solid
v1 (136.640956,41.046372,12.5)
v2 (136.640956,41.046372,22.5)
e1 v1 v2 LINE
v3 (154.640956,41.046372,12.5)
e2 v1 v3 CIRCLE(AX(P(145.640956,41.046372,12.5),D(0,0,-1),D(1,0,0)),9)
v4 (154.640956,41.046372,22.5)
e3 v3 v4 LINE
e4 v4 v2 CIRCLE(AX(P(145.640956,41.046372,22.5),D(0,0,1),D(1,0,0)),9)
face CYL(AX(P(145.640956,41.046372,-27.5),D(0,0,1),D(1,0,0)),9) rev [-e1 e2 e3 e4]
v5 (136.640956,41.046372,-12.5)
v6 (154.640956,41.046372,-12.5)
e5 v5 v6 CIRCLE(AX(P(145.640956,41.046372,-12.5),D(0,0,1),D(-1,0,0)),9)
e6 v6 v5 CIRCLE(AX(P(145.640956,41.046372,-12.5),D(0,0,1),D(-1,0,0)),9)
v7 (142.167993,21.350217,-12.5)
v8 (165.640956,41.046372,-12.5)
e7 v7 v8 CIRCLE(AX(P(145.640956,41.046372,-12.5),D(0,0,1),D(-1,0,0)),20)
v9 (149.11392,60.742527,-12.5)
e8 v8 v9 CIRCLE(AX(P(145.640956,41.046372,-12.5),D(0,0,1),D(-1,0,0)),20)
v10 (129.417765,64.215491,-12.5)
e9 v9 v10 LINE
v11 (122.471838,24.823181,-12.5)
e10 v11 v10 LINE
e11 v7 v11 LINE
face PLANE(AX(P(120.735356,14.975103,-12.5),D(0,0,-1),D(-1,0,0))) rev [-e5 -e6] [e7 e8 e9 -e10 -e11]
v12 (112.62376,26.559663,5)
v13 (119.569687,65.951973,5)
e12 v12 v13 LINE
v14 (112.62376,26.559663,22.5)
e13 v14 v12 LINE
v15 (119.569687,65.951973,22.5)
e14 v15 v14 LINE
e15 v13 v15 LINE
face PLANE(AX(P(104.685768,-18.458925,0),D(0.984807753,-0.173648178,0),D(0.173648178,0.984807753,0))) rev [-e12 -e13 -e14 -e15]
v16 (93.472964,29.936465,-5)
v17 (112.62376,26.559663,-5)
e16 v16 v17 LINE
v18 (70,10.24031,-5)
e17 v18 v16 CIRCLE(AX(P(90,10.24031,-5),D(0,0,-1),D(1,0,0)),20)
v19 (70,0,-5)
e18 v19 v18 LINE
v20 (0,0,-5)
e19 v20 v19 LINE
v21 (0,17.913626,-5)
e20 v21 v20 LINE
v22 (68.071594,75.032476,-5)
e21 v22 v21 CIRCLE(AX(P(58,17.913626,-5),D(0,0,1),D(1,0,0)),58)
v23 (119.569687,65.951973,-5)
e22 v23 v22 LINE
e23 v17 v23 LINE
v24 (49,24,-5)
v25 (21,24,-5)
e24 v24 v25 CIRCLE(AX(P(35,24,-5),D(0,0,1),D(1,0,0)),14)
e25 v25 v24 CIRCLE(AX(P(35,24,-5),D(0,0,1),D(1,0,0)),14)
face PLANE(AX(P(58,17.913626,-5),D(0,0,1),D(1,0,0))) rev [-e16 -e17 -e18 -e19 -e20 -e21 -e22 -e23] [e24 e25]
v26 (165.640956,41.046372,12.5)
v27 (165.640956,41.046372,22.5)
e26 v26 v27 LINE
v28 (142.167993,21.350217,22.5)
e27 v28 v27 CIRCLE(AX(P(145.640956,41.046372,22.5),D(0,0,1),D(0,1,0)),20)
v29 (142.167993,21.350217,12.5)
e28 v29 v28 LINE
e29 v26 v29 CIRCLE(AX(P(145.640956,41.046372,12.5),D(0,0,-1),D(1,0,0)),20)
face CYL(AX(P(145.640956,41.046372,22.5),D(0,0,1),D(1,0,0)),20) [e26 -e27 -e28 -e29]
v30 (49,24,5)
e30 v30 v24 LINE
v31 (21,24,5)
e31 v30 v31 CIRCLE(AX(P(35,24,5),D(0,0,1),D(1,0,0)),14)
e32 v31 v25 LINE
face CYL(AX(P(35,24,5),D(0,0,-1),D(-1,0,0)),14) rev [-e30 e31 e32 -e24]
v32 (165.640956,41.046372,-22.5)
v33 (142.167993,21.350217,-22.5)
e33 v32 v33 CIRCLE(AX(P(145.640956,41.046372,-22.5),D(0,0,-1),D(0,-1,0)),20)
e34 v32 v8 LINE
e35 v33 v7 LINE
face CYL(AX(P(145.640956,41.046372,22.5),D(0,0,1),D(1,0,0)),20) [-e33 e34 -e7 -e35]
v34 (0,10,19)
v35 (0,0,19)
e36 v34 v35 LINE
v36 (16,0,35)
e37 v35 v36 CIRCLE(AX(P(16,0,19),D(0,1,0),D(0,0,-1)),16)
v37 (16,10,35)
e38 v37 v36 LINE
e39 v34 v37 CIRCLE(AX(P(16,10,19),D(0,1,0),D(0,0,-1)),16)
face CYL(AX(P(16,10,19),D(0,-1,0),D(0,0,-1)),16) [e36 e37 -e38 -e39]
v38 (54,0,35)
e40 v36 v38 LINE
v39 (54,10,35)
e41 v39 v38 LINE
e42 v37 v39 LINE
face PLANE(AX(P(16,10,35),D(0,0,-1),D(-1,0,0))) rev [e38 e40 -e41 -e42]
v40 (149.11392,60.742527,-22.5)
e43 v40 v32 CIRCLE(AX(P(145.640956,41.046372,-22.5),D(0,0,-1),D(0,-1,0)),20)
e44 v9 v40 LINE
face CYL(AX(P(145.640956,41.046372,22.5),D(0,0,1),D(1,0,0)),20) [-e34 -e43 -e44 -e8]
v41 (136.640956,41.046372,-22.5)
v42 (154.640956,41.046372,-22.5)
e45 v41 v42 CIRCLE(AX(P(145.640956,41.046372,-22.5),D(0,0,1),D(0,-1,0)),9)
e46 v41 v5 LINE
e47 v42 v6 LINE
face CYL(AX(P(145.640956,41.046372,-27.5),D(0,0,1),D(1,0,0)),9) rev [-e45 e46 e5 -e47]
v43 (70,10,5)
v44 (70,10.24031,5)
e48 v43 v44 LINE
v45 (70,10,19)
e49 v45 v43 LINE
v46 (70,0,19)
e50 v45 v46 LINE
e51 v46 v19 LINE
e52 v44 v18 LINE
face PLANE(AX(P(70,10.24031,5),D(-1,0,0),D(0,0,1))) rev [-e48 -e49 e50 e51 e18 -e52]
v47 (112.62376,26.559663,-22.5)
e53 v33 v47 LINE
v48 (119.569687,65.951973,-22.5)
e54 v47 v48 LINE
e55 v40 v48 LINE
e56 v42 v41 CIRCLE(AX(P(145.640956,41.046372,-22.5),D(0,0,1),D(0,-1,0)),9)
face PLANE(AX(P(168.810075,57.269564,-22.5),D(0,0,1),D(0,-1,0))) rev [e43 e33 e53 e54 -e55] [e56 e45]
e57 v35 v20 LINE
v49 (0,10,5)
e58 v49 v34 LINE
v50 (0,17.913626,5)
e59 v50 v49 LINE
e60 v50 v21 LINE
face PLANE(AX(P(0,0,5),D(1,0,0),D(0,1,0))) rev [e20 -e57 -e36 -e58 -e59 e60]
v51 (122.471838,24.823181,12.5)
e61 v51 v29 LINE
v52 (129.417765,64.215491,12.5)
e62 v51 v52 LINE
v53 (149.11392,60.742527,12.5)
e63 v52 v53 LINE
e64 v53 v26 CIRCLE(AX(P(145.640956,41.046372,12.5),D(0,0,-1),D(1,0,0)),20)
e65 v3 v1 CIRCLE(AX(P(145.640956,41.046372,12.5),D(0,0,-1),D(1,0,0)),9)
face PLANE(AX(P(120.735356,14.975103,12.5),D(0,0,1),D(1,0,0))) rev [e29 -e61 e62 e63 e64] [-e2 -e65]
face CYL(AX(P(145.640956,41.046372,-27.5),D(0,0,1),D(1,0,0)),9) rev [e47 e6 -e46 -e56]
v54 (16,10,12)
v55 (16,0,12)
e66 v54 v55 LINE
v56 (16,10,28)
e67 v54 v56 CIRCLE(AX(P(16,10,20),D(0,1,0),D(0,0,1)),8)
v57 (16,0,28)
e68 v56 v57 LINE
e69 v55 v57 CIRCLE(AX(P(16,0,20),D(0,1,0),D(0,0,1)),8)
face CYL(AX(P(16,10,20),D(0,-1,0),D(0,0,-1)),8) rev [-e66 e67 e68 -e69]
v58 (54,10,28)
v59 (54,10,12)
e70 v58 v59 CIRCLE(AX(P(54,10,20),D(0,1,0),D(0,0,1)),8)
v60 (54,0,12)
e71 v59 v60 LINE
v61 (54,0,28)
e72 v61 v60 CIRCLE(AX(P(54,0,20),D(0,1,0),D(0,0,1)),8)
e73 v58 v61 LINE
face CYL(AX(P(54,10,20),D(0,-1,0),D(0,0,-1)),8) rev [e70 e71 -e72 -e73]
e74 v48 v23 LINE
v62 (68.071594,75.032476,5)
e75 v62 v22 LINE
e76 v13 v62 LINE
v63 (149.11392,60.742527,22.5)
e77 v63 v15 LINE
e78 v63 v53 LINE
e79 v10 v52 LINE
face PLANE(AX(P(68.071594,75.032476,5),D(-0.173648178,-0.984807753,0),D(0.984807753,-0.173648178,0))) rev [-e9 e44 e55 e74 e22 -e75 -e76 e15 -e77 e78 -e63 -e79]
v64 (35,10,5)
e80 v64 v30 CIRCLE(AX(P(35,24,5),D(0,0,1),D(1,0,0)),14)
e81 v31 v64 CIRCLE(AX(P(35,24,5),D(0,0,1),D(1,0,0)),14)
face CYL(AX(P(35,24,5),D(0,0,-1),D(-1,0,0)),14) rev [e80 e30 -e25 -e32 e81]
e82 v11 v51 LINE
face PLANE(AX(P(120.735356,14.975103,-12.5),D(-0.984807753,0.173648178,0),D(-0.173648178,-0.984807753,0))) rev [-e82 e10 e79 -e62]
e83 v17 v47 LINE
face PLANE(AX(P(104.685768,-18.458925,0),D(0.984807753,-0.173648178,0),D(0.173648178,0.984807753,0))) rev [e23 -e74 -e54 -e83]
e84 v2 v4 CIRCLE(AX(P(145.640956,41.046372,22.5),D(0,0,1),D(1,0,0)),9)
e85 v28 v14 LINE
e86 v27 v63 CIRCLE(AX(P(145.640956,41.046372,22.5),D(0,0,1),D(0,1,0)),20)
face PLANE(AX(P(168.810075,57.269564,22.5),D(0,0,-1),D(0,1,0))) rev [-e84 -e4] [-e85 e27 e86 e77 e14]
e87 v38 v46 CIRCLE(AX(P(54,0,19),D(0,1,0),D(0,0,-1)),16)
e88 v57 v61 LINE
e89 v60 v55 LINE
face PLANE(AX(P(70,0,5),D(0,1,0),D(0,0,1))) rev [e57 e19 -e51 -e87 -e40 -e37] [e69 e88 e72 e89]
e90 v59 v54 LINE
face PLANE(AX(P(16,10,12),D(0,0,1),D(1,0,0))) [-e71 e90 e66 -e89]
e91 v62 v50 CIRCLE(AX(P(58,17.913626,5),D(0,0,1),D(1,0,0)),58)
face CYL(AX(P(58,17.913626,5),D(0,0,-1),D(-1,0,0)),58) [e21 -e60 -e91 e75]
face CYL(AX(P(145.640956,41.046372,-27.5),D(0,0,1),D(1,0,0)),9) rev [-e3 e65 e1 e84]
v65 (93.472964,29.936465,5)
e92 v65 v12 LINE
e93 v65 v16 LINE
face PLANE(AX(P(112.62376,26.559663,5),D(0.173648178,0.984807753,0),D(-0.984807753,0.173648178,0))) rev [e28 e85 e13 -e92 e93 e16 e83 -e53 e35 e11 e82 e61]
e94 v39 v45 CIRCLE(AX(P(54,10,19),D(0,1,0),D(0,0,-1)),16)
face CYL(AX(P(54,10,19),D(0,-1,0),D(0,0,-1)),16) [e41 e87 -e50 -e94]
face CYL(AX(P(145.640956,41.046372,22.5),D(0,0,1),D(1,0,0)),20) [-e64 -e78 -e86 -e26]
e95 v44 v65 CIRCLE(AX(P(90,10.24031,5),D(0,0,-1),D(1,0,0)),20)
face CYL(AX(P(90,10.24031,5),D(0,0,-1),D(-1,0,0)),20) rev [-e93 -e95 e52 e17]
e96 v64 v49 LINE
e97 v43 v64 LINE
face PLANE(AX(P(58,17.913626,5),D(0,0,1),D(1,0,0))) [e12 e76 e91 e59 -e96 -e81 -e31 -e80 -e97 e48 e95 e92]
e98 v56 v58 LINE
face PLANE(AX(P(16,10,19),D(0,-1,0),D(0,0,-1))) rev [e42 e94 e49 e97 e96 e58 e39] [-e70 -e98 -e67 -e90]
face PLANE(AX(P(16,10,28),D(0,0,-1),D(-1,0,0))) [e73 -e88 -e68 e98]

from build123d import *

# Parameters (mm, degrees)
ARCHED_PLATE_PROFILE_R      = 14
ARCHED_BASE_PLATE_DEPTH     = 5
SLOTTED_MOUNTING_FOOT_DEPTH = 10
CLEVIS_BLOCK_PROFILE_W      = 45
CLEVIS_BLOCK_PROFILE_H      = 40
CLEVIS_BLOCK_DEPTH          = 50
PLATE_EDGE_FILLET_RADIUS    = 20
PLATE_EDGE_FILLET_LENGTH    = 45
CLEVIS_PIN_HOLE_PROFILE_R   = 9
CLEVIS_PIN_HOLE_18_DEPTH    = 50
CLEVIS_SLOT_PROFILE_W       = 50
CLEVIS_SLOT_PROFILE_H       = 25
CLEVIS_SLOT_DEPTH           = 50


with BuildPart() as part:
    # Arched Plate Profile → Arched Base Plate (new, symmetric)
    with BuildSketch(Plane.XY):
        with BuildLine():
            Line((0, 0), (0, 17.91362622))
            ThreePointArc((0, 17.91362622), (20.718318638, 62.344203921), (68.071594305, 75.032475895))
            Line((68.071594305, 75.032475895), (119.569687178, 65.951972666))
            Line((119.569687178, 65.951972666), (112.623760072, 26.559662546))
            Line((112.623760072, 26.559662546), (93.472963553, 29.936464674))
            ThreePointArc((93.472963553, 29.936464674), (77.144247806, 25.561198476), (70, 10.240309613))
            Line((70, 10.240309613), (70, 0))
            Line((70, 0), (0, 0))
        make_face()
        with Locations((35, 24)):
            Circle(ARCHED_PLATE_PROFILE_R, mode=Mode.SUBTRACT)
    extrude(amount=ARCHED_BASE_PLATE_DEPTH, both=True)

    # Slotted Foot Profile → Slotted Mounting Foot (add)
    with BuildSketch(Plane(origin=(0, 0, 0), x_dir=(1, 0, 0), z_dir=(0, 1, 0))):
        with BuildLine():
            Line((0, -5), (70, -5))
            Line((70, -5), (70, -19))
            ThreePointArc((70, -19), (65.313708499, -30.313708499), (54, -35))
            Line((54, -35), (16, -35))
            ThreePointArc((16, -35), (4.686291501, -30.313708499), (0, -19))
            Line((0, -19), (0, -5))
        make_face()
        with BuildLine():
            Line((16, -12), (54, -12))
            ThreePointArc((54, -12), (62, -20), (54, -28))
            Line((54, -28), (16, -28))
            ThreePointArc((16, -28), (8, -20), (16, -12))
        make_face(mode=Mode.SUBTRACT)
    extrude(amount=SLOTTED_MOUNTING_FOOT_DEPTH)

    # Clevis Block Profile → Clevis Block (add)
    with BuildSketch(Plane(origin=(104.685768373, -18.45892546, 0), x_dir=(0, 0, -1), z_dir=(0.9848077530122075, -0.17364817766693413, 0))):
        with Locations((0, 65.713072291)):
            Rectangle(CLEVIS_BLOCK_PROFILE_W, CLEVIS_BLOCK_PROFILE_H)
    extrude(amount=CLEVIS_BLOCK_DEPTH)

    # Plate Edge Fillet: full round fillet: the end face becomes a half cylinder, R = half its width
    plate_edge_fillet_face = Plane((165.337111276, 37.573408722, 0), x_dir=(0, 0, -1), z_dir=(0.984807753012, -0.173648177667, 0))  # on the end face: x along it, z out of the body
    plate_edge_fillet_slab = plate_edge_fillet_face.offset(-PLATE_EDGE_FILLET_RADIUS / 2) * Box(PLATE_EDGE_FILLET_LENGTH, 2 * PLATE_EDGE_FILLET_RADIUS, PLATE_EDGE_FILLET_RADIUS, mode=Mode.PRIVATE)  # the body's end, R deep
    plate_edge_fillet_round = Plane((145.640956216, 41.046372275, 0), x_dir=(0.984807753012, -0.173648177667, 0), z_dir=(0, 0, -1)) * Cylinder(PLATE_EDGE_FILLET_RADIUS, PLATE_EDGE_FILLET_LENGTH, mode=Mode.PRIVATE)  # its axis R under the face
    add(plate_edge_fillet_slab - plate_edge_fillet_round, mode=Mode.SUBTRACT)

    # Clevis Pin Hole Profile → Clevis Pin Hole _18 (cut)
    with BuildSketch(Plane.XY.offset(22.5)):
        with Locations((145.640956215, 41.046372276)):
            Circle(CLEVIS_PIN_HOLE_PROFILE_R)
    extrude(amount=-CLEVIS_PIN_HOLE_18_DEPTH, mode=Mode.SUBTRACT)

    # Clevis Slot Profile → Clevis Slot (cut)
    with BuildSketch(Plane(origin=(14.883918806, 84.410898126, 0), x_dir=(0.9848077530122074, -0.17364817766693438, 0), z_dir=(0.17364817766693438, 0.9848077530122074, 0))):
        with Locations((141.300715091, 0)):
            Rectangle(CLEVIS_SLOT_PROFILE_W, CLEVIS_SLOT_PROFILE_H)
    extrude(amount=-CLEVIS_SLOT_DEPTH, mode=Mode.SUBTRACT)


solid = part.part
